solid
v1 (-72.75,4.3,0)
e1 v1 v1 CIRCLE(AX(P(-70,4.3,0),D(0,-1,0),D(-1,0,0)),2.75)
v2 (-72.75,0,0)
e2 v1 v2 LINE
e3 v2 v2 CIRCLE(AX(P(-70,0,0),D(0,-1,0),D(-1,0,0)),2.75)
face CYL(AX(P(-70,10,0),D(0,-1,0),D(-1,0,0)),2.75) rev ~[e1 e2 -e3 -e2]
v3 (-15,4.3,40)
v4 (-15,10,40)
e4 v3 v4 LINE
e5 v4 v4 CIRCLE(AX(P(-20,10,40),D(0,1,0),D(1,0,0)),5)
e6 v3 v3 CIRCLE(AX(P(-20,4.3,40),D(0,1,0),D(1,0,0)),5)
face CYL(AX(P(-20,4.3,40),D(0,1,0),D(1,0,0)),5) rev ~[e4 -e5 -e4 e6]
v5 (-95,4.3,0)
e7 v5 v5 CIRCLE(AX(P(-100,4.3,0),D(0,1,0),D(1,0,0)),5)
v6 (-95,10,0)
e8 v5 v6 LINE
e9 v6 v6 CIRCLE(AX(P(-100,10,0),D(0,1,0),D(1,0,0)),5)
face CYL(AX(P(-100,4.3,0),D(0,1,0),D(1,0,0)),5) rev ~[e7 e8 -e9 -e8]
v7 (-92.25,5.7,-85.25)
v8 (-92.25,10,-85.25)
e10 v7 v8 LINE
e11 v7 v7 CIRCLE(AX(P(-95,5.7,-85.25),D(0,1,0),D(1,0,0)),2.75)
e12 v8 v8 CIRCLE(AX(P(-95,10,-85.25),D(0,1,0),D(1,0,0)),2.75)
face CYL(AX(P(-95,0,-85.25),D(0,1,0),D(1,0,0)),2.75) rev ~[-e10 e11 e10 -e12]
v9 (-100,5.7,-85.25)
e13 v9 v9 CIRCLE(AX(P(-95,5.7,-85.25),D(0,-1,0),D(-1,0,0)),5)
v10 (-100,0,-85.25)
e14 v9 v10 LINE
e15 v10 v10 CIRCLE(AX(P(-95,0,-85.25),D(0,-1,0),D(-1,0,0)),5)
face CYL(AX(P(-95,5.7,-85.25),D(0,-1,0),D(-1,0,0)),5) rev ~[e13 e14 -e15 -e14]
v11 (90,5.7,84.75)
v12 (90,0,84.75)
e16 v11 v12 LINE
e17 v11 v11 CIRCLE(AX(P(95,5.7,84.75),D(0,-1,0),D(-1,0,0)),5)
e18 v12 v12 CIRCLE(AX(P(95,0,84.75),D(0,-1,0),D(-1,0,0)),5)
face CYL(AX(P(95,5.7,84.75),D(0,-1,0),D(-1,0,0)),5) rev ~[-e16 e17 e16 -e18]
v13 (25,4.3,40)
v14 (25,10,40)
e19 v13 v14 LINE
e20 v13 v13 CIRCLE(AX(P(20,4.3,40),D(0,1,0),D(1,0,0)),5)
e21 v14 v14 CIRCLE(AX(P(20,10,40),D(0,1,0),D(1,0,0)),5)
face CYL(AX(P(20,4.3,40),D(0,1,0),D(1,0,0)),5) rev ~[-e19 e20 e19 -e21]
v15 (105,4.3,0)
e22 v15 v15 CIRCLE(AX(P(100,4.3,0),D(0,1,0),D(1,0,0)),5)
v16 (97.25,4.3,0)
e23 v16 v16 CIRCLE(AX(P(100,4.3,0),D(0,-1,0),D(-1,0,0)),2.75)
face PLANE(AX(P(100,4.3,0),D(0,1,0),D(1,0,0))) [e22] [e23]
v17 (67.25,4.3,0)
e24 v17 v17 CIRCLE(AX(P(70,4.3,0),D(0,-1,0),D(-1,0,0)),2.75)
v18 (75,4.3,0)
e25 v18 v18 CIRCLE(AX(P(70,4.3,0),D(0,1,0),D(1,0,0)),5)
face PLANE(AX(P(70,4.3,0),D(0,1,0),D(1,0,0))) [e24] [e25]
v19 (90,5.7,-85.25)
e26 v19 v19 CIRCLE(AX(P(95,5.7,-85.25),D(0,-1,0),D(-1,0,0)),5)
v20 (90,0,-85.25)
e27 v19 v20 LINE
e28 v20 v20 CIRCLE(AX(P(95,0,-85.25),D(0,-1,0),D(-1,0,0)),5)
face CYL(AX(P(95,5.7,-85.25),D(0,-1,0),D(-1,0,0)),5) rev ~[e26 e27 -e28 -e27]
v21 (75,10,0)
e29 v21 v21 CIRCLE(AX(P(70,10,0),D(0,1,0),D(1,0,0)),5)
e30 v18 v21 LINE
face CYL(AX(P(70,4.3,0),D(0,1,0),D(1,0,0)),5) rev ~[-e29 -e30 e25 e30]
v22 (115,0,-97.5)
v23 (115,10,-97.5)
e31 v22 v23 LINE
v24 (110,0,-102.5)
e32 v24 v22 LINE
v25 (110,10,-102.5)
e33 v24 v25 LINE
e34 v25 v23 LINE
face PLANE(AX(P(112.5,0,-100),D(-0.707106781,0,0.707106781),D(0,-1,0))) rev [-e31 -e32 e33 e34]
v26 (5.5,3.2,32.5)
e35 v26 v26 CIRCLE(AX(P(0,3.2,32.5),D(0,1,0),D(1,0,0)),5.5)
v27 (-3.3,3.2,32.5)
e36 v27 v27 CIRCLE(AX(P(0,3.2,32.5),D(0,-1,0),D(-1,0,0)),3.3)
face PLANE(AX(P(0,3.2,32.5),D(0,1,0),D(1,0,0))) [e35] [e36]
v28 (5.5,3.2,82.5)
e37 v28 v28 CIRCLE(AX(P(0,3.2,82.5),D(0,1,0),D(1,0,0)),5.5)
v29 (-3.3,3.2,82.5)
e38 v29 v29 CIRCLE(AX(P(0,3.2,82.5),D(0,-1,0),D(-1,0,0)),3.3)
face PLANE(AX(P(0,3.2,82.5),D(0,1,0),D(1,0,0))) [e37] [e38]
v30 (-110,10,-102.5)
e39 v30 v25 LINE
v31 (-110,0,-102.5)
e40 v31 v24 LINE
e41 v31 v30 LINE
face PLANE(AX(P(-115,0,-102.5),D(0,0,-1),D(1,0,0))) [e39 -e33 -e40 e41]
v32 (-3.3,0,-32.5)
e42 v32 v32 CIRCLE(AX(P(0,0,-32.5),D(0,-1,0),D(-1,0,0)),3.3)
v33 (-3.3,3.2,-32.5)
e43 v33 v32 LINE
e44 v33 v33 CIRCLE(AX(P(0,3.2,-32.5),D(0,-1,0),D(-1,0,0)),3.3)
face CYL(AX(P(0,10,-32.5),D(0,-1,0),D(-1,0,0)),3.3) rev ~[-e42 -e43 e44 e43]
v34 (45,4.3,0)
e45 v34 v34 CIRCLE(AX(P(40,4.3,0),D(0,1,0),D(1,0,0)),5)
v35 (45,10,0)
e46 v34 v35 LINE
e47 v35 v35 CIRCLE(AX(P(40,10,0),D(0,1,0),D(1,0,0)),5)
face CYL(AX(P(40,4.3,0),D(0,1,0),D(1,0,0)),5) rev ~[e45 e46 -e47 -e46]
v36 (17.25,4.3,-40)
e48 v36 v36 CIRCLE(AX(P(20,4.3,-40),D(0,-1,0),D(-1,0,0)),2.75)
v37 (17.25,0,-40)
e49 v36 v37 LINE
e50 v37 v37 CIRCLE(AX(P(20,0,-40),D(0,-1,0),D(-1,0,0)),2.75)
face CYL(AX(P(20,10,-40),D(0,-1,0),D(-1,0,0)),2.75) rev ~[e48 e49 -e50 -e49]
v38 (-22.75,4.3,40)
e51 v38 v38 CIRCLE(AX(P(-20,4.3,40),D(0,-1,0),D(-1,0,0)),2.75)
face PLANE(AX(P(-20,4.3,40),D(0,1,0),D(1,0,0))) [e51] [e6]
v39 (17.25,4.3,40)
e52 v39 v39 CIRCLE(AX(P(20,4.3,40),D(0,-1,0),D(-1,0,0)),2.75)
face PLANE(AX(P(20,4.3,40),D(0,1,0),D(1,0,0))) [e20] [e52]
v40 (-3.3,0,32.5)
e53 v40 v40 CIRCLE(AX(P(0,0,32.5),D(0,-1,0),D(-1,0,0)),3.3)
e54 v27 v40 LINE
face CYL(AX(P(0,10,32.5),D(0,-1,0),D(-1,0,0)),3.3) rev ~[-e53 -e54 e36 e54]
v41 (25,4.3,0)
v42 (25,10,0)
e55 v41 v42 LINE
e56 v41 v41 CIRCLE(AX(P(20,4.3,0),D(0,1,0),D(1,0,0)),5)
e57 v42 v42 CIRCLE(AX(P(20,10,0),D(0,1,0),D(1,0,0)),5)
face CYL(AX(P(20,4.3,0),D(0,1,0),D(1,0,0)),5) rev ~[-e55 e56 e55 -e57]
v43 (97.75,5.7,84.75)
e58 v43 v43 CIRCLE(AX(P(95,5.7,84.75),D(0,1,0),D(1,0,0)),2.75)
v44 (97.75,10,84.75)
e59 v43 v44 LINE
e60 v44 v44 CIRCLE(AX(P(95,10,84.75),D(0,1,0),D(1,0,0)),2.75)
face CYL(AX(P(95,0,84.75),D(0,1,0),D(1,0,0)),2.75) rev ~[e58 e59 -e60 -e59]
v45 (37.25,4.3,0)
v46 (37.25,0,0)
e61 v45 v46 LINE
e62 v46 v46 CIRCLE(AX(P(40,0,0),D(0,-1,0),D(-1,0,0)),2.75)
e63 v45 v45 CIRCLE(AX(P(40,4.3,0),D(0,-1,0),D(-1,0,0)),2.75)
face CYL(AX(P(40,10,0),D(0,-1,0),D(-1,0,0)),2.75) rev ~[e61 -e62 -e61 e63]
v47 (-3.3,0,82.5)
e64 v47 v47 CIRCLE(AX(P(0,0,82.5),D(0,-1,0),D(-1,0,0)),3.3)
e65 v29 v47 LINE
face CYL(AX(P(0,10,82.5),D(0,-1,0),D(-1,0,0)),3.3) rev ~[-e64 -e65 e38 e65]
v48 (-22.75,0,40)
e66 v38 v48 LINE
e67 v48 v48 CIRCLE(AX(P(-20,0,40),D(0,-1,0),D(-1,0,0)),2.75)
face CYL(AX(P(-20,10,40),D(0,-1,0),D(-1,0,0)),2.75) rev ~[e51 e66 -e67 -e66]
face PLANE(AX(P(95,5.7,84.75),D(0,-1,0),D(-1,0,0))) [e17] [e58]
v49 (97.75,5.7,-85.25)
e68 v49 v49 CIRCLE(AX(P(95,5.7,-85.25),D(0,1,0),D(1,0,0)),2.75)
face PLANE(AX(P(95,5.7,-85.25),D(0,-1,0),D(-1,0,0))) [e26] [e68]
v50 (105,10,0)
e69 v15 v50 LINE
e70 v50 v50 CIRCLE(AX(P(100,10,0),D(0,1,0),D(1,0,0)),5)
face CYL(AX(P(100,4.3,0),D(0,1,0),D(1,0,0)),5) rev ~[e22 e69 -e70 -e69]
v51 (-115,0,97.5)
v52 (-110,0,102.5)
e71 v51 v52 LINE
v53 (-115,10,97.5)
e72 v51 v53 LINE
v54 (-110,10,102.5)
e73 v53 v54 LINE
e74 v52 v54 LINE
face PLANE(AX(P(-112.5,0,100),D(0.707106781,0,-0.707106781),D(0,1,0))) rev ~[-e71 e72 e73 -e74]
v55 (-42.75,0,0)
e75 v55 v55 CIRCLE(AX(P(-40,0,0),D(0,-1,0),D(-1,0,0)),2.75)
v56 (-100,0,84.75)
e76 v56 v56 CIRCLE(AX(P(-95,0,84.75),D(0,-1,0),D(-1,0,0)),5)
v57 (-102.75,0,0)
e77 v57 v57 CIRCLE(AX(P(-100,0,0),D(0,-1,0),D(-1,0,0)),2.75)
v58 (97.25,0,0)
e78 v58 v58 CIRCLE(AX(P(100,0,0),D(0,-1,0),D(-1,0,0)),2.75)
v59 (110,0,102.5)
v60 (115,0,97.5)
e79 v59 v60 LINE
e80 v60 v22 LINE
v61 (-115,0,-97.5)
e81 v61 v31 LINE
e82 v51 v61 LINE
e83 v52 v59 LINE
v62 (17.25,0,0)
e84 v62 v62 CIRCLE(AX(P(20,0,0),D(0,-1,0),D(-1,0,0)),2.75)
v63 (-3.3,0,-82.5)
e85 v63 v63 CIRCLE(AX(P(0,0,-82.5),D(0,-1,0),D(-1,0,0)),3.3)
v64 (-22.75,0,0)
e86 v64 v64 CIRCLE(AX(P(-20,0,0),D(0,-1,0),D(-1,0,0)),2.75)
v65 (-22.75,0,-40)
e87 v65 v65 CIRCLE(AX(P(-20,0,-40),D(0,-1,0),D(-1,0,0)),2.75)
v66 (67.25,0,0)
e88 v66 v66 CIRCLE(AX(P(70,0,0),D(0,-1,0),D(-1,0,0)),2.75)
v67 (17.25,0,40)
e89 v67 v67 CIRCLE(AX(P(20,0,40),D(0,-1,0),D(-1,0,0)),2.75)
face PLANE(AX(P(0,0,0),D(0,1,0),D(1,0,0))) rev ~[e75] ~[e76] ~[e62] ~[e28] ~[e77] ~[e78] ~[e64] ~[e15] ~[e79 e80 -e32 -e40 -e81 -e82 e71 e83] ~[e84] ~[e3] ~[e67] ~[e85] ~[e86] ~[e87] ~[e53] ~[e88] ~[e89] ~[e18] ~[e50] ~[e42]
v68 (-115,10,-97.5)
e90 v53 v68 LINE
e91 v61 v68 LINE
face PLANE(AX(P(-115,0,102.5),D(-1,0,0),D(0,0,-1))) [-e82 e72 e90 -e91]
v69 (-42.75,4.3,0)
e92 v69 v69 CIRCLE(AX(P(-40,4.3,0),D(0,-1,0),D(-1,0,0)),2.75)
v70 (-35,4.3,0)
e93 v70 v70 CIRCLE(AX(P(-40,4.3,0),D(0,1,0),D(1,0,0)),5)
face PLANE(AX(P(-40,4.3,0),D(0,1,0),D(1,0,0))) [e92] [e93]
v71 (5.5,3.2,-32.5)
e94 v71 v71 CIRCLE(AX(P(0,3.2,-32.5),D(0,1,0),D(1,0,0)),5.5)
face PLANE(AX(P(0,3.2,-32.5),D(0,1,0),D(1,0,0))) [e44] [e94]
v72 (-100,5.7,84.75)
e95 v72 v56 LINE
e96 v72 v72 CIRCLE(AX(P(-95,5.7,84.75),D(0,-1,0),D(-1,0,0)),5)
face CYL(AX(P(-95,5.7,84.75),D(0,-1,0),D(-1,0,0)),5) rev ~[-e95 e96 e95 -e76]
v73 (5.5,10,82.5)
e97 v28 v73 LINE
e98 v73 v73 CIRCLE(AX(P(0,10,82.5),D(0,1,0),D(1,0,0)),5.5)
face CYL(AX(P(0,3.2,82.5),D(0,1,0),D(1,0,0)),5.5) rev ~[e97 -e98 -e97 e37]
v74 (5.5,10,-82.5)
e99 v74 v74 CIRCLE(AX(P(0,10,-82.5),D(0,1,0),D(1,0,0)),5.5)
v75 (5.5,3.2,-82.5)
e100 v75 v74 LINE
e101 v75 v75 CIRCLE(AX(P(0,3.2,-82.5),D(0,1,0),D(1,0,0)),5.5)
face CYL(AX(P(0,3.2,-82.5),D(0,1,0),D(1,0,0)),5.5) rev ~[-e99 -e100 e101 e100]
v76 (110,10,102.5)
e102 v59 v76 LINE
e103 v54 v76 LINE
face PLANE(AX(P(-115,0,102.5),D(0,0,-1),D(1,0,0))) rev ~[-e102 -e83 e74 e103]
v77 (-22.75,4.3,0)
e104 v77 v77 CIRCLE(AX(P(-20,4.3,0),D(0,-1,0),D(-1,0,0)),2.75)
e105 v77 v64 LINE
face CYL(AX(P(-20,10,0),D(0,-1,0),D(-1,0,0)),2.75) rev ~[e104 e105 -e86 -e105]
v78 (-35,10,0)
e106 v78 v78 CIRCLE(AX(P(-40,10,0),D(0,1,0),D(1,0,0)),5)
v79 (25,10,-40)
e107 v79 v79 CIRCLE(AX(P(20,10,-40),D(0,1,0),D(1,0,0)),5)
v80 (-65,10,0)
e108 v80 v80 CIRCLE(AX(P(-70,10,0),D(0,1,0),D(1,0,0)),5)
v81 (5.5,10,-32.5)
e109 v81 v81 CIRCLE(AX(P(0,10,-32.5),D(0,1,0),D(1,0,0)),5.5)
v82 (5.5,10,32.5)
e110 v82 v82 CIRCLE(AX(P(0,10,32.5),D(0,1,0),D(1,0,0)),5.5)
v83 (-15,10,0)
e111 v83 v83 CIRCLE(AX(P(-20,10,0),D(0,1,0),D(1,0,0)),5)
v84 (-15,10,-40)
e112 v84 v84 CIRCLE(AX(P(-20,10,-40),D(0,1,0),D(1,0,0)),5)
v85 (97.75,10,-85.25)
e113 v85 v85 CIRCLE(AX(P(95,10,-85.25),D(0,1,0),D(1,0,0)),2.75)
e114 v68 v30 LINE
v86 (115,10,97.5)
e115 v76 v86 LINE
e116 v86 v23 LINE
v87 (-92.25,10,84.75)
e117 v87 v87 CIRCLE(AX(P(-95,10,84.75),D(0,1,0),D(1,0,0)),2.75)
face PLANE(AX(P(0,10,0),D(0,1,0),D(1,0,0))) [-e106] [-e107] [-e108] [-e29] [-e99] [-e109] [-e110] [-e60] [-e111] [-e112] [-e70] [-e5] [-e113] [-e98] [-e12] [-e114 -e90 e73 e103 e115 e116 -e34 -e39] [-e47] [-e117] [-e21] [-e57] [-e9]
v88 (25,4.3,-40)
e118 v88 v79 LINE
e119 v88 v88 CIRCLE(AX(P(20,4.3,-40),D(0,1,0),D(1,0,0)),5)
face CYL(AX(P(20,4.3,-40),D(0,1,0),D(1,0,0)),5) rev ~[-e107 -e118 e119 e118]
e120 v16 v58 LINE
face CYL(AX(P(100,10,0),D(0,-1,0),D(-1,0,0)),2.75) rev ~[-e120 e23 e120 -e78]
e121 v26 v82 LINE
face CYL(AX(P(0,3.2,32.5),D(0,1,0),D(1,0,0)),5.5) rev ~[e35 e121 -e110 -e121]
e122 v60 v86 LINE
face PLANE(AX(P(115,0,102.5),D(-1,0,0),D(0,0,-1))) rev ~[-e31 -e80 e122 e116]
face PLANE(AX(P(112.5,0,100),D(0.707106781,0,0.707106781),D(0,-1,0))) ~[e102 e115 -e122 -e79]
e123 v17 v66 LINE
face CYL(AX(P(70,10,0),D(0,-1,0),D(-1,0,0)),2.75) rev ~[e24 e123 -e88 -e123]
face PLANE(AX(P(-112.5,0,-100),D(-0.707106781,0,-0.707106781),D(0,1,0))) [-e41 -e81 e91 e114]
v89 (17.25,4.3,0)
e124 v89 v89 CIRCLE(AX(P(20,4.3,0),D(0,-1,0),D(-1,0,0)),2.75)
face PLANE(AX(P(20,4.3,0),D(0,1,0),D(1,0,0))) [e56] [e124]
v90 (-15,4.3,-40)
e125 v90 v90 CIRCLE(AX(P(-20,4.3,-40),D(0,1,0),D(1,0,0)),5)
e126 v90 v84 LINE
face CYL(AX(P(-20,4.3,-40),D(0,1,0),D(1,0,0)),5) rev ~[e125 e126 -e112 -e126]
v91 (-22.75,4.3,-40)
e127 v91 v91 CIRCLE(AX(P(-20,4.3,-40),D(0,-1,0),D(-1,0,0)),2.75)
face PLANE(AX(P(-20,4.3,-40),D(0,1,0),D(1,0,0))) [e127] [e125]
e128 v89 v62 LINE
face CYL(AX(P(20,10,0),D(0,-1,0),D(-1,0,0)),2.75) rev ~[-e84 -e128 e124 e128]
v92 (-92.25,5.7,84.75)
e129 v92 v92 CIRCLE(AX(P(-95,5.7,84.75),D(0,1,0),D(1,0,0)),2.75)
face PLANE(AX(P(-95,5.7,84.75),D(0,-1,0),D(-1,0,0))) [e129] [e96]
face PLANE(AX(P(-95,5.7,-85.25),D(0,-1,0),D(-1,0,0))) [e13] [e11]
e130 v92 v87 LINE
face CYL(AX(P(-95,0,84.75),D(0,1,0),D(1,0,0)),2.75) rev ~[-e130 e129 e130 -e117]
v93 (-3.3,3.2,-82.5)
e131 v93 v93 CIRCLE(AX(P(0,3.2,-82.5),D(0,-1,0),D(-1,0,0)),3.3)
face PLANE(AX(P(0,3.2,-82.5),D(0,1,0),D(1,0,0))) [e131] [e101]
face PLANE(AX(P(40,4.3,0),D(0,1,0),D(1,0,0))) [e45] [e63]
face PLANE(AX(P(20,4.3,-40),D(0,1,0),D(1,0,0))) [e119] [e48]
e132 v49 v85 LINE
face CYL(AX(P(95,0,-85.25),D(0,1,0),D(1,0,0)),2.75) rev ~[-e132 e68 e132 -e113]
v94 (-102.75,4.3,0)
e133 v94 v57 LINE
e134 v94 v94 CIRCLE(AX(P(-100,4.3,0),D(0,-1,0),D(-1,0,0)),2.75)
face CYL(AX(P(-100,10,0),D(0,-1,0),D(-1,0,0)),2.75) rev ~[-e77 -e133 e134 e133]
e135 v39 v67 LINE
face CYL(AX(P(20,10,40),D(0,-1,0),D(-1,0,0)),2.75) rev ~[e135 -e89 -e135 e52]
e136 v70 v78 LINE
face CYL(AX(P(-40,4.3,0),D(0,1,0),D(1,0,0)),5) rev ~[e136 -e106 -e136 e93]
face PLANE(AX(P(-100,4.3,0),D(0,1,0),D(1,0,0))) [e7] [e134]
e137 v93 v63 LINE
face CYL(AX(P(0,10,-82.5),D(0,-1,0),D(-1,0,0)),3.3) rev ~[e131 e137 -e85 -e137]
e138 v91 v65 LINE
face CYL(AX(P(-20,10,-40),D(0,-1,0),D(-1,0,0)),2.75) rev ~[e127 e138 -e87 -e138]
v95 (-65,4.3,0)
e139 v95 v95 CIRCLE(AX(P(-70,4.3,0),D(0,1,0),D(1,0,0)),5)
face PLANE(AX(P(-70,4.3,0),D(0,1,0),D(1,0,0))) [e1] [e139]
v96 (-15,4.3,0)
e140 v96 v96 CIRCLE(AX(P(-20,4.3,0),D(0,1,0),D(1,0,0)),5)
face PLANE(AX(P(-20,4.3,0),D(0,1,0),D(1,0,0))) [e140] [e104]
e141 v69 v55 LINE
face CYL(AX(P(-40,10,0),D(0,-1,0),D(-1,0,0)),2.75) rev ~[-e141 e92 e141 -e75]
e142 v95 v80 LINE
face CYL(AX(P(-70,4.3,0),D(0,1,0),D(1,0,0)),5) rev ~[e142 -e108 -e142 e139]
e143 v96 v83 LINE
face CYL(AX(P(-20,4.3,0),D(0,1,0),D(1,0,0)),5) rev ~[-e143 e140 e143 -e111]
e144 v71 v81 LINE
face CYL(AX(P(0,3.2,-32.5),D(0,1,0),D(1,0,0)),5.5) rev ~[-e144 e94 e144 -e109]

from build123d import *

# Parameters (mm, degrees)
SKETCH_1_W                = 230
SKETCH_1_H                = 205
EXTRUDE_1_DEPTH           = 10
HOLE_WIZARD_1_D           = 5.5
HOLE_WIZARD_1_DEPTH       = 12.4
HOLE_WIZARD_1_CBORE_D     = 10
HOLE_WIZARD_1_CBORE_DEPTH = 5.7
HOLE_WIZARD_1_TIP         = 1.652366702
HOLE_WIZARD_2_D           = 5.5
HOLE_WIZARD_2_DEPTH       = 12.4
HOLE_WIZARD_2_CBORE_D     = 10
HOLE_WIZARD_2_CBORE_DEPTH = 5.7
HOLE_WIZARD_2_TIP         = 1.652366702
CHAMFER_1_SIZE            = 5
HOLE_WIZARD_3_D           = 6.6
HOLE_WIZARD_3_DEPTH       = 12.4
HOLE_WIZARD_3_CBORE_D     = 11
HOLE_WIZARD_3_CBORE_DEPTH = 6.8
HOLE_WIZARD_3_TIP         = 1.982840043


with BuildPart() as part:
    # 草图1 → 凸台-拉伸1 (new body)
    with BuildSketch(Plane(origin=(0, 0, 0), x_dir=(1, 0, 0), z_dir=(0, 1, 0))):
        Rectangle(SKETCH_1_W, SKETCH_1_H)
    extrude(amount=EXTRUDE_1_DEPTH)

    # 打孔尺寸(%根据)内六角圆柱头螺钉的类型1
    with Locations(Plane(origin=(0, 0, 0), x_dir=(-1, 0, 0), z_dir=(0, -1, 0))):
        with Locations((-95, -84.75), (-95, 85.25), (95, -84.75), (95, 85.25)):
            CounterBoreHole(HOLE_WIZARD_1_D / 2, HOLE_WIZARD_1_CBORE_D / 2, HOLE_WIZARD_1_CBORE_DEPTH, depth=HOLE_WIZARD_1_DEPTH)
            with Locations((0, 0, -(HOLE_WIZARD_1_DEPTH + HOLE_WIZARD_1_TIP / 2))):  # 118° drill point
                Cone(0, HOLE_WIZARD_1_D / 2, HOLE_WIZARD_1_TIP, mode=Mode.SUBTRACT)

    # 打孔尺寸(%根据)内六角圆柱头螺钉的类型2
    with Locations(Plane(origin=(0, 10, 0), x_dir=(1, 0, 0), z_dir=(0, 1, 0))):
        with Locations((-100, 0), (-70, 0), (-40, 0), (-20, 0), (-20, 40), (-20, -40), (20, -40), (40, 0), (20, 0), (70, 0), (100, 0), (20, 40)):
            CounterBoreHole(HOLE_WIZARD_2_D / 2, HOLE_WIZARD_2_CBORE_D / 2, HOLE_WIZARD_2_CBORE_DEPTH, depth=HOLE_WIZARD_2_DEPTH)
            with Locations((0, 0, -(HOLE_WIZARD_2_DEPTH + HOLE_WIZARD_2_TIP / 2))):  # 118° drill point
                Cone(0, HOLE_WIZARD_2_D / 2, HOLE_WIZARD_2_TIP, mode=Mode.SUBTRACT)

    # 倒角1
    chamfer_1_edges = [part.edges().sort_by_distance(p)[0] for p in [
        (115, 5, 102.5),
        (-115, 5, 102.5),
        (-115, 5, -102.5),
        (115, 5, -102.5),
    ]]
    chamfer(chamfer_1_edges, length=CHAMFER_1_SIZE)

    # 打孔尺寸(%根据)内六角圆柱头螺钉的类型3
    with Locations(Plane(origin=(0, 10, 0), x_dir=(1, 0, 0), z_dir=(0, 1, 0))):
        with Locations((0, 82.5), (0, 32.5), (0, -32.5), (0, -82.5)):
            CounterBoreHole(HOLE_WIZARD_3_D / 2, HOLE_WIZARD_3_CBORE_D / 2, HOLE_WIZARD_3_CBORE_DEPTH, depth=HOLE_WIZARD_3_DEPTH)
            with Locations((0, 0, -(HOLE_WIZARD_3_DEPTH + HOLE_WIZARD_3_TIP / 2))):  # 118° drill point
                Cone(0, HOLE_WIZARD_3_D / 2, HOLE_WIZARD_3_TIP, mode=Mode.SUBTRACT)


solid = part.part
